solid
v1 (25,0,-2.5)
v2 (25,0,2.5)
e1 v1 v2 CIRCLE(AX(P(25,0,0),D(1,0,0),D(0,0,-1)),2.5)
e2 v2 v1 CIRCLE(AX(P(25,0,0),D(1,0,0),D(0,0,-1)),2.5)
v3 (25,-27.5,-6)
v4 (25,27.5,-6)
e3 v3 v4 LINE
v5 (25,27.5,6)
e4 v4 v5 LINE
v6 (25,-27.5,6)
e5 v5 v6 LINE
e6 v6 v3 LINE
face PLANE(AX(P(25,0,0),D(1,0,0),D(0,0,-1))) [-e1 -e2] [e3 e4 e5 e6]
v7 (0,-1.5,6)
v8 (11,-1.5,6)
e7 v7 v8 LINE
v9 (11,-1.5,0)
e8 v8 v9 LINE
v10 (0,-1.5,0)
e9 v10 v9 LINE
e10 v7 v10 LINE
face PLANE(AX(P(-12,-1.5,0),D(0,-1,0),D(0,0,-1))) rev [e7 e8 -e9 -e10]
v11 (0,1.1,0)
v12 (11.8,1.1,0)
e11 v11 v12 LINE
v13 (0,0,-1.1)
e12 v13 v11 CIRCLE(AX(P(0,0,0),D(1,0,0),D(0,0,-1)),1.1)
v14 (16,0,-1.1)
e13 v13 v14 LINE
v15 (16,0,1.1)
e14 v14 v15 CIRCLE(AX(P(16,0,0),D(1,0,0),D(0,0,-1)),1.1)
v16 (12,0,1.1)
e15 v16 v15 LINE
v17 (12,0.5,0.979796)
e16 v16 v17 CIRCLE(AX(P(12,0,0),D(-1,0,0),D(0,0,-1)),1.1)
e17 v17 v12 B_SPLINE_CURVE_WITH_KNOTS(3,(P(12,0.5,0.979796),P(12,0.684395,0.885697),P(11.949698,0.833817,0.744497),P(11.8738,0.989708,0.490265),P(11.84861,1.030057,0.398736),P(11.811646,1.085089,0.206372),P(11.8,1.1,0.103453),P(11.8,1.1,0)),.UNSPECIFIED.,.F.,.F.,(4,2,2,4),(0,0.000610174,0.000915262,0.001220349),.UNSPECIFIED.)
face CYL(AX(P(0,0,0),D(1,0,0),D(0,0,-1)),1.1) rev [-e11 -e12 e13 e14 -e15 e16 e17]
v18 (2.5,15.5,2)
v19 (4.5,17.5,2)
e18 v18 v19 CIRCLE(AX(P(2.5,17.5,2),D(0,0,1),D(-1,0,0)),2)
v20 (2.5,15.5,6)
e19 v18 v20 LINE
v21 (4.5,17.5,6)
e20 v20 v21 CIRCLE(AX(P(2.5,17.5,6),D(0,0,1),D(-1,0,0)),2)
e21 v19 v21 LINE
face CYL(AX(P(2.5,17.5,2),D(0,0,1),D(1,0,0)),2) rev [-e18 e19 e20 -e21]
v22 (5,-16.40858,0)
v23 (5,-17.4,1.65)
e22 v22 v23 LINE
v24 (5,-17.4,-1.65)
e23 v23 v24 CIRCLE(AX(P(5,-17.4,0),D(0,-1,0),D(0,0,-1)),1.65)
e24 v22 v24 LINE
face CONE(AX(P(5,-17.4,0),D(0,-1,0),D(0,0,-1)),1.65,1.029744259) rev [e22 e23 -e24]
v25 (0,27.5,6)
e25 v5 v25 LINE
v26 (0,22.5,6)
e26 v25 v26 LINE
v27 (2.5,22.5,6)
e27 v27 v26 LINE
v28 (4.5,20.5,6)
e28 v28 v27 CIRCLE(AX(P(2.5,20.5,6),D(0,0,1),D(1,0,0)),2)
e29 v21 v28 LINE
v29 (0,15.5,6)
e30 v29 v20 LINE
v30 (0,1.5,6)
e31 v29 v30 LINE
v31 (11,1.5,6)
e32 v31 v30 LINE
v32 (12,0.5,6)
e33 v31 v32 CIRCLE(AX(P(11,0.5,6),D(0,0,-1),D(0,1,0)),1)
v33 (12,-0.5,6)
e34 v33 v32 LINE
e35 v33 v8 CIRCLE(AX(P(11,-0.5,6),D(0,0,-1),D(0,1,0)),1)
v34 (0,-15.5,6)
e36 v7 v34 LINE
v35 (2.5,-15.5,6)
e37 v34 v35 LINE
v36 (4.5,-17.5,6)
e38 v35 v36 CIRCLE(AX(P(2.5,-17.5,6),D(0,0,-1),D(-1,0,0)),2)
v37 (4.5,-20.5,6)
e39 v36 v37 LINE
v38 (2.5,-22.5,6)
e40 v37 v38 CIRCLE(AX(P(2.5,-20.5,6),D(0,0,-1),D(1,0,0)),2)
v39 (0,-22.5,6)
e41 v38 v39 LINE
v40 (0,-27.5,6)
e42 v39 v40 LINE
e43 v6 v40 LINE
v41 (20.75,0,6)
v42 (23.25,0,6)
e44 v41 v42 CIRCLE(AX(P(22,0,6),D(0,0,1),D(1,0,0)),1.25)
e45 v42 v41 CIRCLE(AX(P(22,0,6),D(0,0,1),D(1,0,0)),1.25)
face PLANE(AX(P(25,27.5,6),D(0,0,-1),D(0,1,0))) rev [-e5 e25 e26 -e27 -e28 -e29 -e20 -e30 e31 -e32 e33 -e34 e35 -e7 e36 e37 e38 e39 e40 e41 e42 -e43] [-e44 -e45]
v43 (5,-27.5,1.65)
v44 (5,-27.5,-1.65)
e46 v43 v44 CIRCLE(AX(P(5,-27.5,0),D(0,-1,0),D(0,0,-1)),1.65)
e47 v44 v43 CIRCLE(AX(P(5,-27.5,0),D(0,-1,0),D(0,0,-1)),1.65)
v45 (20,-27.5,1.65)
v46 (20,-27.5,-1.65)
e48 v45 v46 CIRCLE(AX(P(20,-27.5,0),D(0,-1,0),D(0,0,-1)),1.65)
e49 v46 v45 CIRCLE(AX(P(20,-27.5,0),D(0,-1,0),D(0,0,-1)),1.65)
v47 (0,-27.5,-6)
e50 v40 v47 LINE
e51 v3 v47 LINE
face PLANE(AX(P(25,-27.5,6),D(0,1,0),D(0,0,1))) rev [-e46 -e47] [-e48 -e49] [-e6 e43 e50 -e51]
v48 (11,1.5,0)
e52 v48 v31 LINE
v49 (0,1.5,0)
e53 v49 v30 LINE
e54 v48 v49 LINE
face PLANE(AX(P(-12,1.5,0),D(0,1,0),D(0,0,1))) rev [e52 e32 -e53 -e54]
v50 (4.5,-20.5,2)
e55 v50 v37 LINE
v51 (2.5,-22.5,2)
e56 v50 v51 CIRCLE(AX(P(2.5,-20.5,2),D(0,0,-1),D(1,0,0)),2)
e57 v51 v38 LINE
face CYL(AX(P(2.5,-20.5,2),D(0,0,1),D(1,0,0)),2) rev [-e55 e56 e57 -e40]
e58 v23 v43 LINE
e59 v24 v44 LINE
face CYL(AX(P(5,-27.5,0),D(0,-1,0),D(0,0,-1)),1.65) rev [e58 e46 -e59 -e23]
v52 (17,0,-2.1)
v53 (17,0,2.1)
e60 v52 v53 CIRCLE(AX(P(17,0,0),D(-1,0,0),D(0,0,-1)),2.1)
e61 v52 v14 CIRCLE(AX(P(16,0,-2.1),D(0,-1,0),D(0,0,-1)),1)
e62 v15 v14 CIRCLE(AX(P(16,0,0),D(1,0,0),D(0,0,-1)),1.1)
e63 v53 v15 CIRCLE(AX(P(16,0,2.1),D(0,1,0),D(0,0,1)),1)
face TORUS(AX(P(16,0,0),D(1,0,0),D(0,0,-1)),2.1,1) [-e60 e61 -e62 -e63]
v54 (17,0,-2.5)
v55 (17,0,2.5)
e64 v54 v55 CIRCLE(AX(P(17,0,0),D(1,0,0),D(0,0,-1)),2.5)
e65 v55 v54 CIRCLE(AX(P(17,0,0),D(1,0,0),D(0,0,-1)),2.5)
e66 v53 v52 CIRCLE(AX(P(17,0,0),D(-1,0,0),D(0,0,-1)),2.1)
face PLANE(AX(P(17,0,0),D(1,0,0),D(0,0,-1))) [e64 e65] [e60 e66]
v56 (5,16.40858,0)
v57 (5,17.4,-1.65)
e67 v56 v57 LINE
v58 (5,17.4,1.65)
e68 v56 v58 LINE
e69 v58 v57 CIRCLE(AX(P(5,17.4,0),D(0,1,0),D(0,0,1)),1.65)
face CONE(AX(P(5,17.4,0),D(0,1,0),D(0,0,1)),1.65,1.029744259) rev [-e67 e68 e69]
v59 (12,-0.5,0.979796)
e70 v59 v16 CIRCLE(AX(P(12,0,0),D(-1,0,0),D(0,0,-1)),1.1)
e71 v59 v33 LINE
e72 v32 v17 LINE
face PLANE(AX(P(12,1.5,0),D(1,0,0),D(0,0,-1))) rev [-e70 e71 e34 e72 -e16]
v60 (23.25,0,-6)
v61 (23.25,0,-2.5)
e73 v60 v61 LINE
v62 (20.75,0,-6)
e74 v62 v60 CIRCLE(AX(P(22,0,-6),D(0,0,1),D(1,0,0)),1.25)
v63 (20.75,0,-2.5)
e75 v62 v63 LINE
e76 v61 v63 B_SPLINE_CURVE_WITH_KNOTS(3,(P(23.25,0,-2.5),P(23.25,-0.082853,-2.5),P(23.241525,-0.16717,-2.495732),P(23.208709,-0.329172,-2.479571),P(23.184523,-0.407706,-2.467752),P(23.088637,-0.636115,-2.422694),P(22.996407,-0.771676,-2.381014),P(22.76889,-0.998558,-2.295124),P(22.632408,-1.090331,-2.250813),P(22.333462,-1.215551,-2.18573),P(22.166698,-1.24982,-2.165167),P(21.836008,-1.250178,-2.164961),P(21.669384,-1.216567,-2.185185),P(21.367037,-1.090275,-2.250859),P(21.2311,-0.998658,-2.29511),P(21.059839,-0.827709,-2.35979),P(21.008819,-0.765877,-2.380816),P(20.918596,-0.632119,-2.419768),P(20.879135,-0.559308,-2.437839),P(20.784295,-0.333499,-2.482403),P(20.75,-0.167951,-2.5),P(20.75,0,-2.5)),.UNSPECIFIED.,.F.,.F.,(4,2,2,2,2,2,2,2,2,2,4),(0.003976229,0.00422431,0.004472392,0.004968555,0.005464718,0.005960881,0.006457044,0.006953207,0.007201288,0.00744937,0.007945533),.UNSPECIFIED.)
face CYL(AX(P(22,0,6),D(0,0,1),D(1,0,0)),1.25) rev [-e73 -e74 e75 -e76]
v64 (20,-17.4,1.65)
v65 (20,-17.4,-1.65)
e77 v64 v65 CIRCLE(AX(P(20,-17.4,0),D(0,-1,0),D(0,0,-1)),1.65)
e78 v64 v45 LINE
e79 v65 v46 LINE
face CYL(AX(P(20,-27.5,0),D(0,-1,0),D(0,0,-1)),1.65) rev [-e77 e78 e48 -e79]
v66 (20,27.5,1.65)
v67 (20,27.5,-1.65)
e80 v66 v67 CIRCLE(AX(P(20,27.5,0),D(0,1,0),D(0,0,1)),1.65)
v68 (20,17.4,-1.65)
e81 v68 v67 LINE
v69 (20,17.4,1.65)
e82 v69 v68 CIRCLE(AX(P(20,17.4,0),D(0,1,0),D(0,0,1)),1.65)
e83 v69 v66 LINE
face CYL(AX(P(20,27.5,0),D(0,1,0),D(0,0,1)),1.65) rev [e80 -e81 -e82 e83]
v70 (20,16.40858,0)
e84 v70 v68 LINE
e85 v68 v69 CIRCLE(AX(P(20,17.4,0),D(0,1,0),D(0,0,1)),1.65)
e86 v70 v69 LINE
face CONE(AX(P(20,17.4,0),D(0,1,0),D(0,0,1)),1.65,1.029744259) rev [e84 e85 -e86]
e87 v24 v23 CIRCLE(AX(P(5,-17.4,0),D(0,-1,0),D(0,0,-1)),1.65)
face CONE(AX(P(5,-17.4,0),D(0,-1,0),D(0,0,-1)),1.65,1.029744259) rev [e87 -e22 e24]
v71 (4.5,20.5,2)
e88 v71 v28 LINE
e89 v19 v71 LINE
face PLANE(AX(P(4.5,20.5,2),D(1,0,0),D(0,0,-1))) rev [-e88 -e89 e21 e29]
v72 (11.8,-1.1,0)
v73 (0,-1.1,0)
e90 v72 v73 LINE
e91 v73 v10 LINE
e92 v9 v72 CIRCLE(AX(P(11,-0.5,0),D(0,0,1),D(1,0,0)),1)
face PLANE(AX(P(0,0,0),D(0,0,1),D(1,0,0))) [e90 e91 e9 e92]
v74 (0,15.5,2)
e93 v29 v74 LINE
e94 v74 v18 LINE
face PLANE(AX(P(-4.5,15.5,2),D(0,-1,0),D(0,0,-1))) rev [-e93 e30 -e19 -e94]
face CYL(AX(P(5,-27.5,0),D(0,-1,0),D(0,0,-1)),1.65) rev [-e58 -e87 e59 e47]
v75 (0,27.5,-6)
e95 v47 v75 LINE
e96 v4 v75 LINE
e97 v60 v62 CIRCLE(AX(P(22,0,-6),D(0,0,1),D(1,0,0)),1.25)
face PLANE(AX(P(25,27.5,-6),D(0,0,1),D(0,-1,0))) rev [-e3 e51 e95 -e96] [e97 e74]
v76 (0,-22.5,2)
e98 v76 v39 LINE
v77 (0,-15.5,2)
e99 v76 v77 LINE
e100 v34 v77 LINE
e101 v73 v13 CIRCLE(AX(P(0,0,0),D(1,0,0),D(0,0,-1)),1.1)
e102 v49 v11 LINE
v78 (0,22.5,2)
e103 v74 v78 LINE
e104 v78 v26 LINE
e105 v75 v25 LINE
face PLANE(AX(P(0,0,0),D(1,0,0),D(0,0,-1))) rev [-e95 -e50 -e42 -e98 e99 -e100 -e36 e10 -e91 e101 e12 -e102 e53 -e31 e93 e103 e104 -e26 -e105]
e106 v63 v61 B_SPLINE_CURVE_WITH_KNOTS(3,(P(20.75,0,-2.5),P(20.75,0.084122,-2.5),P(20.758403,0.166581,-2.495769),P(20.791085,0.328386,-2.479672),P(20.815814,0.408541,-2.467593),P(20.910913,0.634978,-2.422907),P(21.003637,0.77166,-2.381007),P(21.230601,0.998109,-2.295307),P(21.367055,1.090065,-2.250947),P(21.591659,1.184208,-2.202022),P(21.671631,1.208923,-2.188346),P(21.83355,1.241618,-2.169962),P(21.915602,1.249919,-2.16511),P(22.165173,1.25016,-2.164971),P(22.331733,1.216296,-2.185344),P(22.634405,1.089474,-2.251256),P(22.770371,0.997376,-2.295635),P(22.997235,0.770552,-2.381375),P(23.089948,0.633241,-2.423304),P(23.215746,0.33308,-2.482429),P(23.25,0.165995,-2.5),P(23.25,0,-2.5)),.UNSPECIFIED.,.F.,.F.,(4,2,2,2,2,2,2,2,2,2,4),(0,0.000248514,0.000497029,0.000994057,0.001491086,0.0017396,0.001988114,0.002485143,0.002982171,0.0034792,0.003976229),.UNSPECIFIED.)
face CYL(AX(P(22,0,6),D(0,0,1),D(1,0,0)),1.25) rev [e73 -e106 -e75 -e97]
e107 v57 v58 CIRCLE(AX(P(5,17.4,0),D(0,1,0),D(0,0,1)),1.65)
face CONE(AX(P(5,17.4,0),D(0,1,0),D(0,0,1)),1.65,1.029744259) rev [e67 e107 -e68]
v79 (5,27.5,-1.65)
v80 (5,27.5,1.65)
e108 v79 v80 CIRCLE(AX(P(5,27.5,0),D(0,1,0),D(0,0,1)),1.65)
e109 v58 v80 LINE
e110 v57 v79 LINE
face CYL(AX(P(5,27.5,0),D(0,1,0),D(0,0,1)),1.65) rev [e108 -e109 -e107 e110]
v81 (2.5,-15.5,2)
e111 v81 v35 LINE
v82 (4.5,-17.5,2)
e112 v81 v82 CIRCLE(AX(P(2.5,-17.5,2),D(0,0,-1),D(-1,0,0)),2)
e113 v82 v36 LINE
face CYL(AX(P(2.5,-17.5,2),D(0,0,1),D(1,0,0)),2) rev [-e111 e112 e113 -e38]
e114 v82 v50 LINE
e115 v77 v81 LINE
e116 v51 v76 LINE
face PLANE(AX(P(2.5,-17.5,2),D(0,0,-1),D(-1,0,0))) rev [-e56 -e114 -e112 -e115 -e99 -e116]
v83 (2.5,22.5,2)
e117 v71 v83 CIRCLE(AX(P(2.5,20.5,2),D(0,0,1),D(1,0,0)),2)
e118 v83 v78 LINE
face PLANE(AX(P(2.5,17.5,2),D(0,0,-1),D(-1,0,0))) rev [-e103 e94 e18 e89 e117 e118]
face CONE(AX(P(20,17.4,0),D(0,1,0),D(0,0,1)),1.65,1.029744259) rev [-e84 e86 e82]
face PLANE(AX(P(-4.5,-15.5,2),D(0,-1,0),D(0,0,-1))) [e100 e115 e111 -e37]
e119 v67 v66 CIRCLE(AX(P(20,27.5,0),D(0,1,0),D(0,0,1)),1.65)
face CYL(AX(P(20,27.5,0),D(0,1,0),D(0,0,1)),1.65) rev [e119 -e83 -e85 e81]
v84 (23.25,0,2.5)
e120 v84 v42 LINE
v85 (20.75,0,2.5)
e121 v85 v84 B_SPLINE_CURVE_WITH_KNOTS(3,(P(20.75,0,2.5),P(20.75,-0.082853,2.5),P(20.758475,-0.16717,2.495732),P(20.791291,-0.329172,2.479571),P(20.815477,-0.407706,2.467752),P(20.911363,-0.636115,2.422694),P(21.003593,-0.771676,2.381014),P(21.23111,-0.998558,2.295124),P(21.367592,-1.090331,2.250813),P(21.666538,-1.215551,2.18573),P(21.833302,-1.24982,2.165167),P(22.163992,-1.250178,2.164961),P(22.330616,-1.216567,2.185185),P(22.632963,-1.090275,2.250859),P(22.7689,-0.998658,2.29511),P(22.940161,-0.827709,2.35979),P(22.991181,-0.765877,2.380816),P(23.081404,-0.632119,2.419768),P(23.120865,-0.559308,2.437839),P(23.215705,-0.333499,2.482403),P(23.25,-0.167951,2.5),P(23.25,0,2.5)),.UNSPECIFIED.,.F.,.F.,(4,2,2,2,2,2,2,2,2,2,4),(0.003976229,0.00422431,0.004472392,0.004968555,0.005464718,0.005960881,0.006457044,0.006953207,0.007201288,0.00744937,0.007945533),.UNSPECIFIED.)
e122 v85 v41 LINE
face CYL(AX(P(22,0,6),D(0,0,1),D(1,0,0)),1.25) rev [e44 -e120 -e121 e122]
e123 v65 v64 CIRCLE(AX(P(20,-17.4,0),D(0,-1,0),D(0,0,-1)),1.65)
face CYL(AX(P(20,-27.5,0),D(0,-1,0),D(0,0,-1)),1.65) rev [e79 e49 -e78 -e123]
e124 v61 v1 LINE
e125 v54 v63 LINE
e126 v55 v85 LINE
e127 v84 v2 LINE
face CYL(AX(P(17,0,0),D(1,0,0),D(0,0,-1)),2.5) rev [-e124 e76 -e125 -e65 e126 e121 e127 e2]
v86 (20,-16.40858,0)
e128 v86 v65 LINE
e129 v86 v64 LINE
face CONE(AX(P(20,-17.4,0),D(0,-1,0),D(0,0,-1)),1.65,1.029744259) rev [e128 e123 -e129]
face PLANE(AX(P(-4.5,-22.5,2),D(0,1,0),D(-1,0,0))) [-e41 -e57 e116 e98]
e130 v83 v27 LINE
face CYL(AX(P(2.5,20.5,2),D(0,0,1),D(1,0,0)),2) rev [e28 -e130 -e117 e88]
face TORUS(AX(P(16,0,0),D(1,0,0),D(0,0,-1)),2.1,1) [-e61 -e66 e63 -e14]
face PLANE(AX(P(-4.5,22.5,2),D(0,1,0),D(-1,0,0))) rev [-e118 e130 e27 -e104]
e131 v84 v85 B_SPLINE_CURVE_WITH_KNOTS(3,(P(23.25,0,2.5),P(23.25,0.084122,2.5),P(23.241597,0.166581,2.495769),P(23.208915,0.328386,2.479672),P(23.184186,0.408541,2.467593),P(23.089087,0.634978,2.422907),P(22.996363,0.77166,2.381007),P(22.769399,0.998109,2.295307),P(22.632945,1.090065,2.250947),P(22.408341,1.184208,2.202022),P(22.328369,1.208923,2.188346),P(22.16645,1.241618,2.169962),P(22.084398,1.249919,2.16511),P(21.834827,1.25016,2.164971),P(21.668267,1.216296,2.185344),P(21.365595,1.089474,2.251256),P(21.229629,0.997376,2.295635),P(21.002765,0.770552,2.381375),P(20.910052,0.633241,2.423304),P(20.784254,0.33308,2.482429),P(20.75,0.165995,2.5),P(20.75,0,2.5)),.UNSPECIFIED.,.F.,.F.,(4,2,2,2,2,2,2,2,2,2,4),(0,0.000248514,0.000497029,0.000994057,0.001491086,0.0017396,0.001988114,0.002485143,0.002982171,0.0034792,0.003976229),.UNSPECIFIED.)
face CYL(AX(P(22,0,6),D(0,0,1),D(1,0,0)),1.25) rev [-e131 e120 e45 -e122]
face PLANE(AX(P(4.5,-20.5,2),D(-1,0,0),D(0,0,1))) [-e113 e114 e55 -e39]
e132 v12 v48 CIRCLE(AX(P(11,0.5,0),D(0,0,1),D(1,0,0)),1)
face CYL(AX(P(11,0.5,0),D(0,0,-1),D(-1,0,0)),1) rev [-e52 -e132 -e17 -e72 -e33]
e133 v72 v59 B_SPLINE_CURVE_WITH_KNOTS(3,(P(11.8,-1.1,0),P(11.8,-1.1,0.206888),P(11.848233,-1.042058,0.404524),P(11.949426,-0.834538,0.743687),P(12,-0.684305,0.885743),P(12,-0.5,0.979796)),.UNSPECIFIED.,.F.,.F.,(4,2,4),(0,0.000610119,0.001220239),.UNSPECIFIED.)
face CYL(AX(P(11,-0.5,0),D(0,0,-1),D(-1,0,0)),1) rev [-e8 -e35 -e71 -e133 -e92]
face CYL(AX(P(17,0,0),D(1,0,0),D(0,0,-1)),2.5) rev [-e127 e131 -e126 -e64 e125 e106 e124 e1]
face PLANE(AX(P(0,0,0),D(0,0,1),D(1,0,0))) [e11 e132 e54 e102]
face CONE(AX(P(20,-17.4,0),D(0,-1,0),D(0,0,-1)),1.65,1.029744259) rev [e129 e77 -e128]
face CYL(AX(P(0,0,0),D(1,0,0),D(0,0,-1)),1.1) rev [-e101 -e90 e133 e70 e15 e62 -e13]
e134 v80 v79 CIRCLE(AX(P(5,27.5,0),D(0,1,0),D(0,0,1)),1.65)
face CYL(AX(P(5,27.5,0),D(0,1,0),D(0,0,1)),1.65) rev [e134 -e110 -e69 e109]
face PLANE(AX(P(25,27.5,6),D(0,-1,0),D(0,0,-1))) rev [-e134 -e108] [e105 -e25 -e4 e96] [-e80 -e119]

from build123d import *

# Parameters (mm, degrees)
SKETCH_1_W                  = 12
SKETCH_1_H                  = 55
EXTRUDE_1_DEPTH             = 25
SKETCH_2_R                  = 1.1
CUT_EXTRUDE_1_DEPTH         = 25
SKETCH_3_R                  = 2.5
CUT_EXTRUDE_2_DEPTH         = 8
SKETCH_4_W                  = 24
SKETCH_4_H                  = 3
CUT_EXTRUDE_3_DEPTH         = 6
HOLE_WIZARD_M4_1_AT_2_COUNT = 2
HOLE_WIZARD_M4_1_AT_2_PITCH = 15
FILLET_1_R                  = 1
CUT_EXTRUDE_4_DEPTH         = 4
HOLE_WIZARD_M3_1_D          = 2.5
FILLET_2_R                  = 1


with BuildPart() as part:
    # 草图1 → 凸台-拉伸1 (new body)
    with BuildSketch(Plane(origin=(0, 0, 0), x_dir=(0, 0, -1), z_dir=(1, 0, 0))):
        Rectangle(SKETCH_1_W, SKETCH_1_H)
    extrude(amount=EXTRUDE_1_DEPTH)

    # 草图2 → 切除-拉伸1 (cut)
    with BuildSketch(Plane(origin=(25, 0, 0), x_dir=(0, 0, -1), z_dir=(1, 0, 0))):
        Circle(SKETCH_2_R)
    extrude(amount=-CUT_EXTRUDE_1_DEPTH, mode=Mode.SUBTRACT)

    # 草图3 → 切除-拉伸2 (cut)
    with BuildSketch(Plane(origin=(25, 0, 0), x_dir=(0, 0, -1), z_dir=(1, 0, 0))):
        Circle(SKETCH_3_R)
    extrude(amount=-CUT_EXTRUDE_2_DEPTH, mode=Mode.SUBTRACT)

    # 草图4 → 切除-拉伸3 (cut)
    with BuildSketch(Plane.XY.offset(6)):
        Rectangle(SKETCH_4_W, SKETCH_4_H)
    extrude(amount=-CUT_EXTRUDE_3_DEPTH, mode=Mode.SUBTRACT)

    # 草图7 → M4 螺纹孔1 (revolve, cut)
    with BuildSketch(Plane(origin=(5, 27.5, 0), x_dir=(0, 0, 1), z_dir=(1, 0, 0))):
        Polygon((0, 0), (0, 11.091420021), (1.65, 10.1), (1.65, 0), align=None)
    hole_wizard_m4_1 = revolve(axis=Axis((5, 33.85, 0), (0, -1, 0)), mode=Mode.SUBTRACT)

    # M4 螺纹孔1 at 2: M4 螺纹孔1 ×2
    with Locations(*[(i * HOLE_WIZARD_M4_1_AT_2_PITCH, 0, 0) for i in range(1, HOLE_WIZARD_M4_1_AT_2_COUNT)]):
        add(hole_wizard_m4_1, mode=Mode.SUBTRACT)

    # 镜向1: M4 螺纹孔1 across plane
    add(hole_wizard_m4_1.mirror(Plane.ZX), mode=Mode.SUBTRACT)

    # 镜向1 copy 1 sketch → 镜向1 copy 1 (revolve, cut)
    with BuildSketch(Plane(origin=(20, -27.5, 0), x_dir=(0, 0, 1), z_dir=(1, 0, 0))):
        Polygon((0, 0), (0, -11.091420021), (1.65, -10.1), (1.65, 0), align=None)
    revolve(axis=Axis((20, -33.85, 0), (0, -1, 0)), mode=Mode.SUBTRACT)

    # 圆角1
    fillet_1_edges = [part.edges().sort_by_distance(p)[0] for p in [
        (12, -1.5, 3),
        (12, 1.5, 3),
    ]]
    fillet(fillet_1_edges, radius=FILLET_1_R)

    # 草图9 → 切除-拉伸4 (cut)
    with BuildSketch(Plane.XY.offset(6)):
        with BuildLine():
            Line((-4.5, 22.5), (2.5, 22.5))
            ThreePointArc((2.5, 22.5), (3.914213562, 21.914213562), (4.5, 20.5))
            Line((4.5, 20.5), (4.5, 17.5))
            ThreePointArc((4.5, 17.5), (3.914213562, 16.085786438), (2.5, 15.5))
            Line((2.5, 15.5), (-4.5, 15.5))
            Line((-4.5, 15.5), (-4.5, 22.5))
        make_face()
    cut_extrude_4 = extrude(amount=-CUT_EXTRUDE_4_DEPTH, mode=Mode.SUBTRACT)

    # 镜向2: 切除-拉伸4 across plane
    add(cut_extrude_4.mirror(Plane.ZX), mode=Mode.SUBTRACT)

    # M3 螺纹孔1 (through all)
    with Locations(Plane.XY.offset(6)):
        with Locations((22, 0)):
            Hole(HOLE_WIZARD_M3_1_D / 2)

    # 圆角2
    fillet_2_edges = [part.edges().sort_by_distance(p)[0] for p in [
        (17, 0, 1.1),
    ]]
    fillet(fillet_2_edges, radius=FILLET_2_R)


solid = part.part
